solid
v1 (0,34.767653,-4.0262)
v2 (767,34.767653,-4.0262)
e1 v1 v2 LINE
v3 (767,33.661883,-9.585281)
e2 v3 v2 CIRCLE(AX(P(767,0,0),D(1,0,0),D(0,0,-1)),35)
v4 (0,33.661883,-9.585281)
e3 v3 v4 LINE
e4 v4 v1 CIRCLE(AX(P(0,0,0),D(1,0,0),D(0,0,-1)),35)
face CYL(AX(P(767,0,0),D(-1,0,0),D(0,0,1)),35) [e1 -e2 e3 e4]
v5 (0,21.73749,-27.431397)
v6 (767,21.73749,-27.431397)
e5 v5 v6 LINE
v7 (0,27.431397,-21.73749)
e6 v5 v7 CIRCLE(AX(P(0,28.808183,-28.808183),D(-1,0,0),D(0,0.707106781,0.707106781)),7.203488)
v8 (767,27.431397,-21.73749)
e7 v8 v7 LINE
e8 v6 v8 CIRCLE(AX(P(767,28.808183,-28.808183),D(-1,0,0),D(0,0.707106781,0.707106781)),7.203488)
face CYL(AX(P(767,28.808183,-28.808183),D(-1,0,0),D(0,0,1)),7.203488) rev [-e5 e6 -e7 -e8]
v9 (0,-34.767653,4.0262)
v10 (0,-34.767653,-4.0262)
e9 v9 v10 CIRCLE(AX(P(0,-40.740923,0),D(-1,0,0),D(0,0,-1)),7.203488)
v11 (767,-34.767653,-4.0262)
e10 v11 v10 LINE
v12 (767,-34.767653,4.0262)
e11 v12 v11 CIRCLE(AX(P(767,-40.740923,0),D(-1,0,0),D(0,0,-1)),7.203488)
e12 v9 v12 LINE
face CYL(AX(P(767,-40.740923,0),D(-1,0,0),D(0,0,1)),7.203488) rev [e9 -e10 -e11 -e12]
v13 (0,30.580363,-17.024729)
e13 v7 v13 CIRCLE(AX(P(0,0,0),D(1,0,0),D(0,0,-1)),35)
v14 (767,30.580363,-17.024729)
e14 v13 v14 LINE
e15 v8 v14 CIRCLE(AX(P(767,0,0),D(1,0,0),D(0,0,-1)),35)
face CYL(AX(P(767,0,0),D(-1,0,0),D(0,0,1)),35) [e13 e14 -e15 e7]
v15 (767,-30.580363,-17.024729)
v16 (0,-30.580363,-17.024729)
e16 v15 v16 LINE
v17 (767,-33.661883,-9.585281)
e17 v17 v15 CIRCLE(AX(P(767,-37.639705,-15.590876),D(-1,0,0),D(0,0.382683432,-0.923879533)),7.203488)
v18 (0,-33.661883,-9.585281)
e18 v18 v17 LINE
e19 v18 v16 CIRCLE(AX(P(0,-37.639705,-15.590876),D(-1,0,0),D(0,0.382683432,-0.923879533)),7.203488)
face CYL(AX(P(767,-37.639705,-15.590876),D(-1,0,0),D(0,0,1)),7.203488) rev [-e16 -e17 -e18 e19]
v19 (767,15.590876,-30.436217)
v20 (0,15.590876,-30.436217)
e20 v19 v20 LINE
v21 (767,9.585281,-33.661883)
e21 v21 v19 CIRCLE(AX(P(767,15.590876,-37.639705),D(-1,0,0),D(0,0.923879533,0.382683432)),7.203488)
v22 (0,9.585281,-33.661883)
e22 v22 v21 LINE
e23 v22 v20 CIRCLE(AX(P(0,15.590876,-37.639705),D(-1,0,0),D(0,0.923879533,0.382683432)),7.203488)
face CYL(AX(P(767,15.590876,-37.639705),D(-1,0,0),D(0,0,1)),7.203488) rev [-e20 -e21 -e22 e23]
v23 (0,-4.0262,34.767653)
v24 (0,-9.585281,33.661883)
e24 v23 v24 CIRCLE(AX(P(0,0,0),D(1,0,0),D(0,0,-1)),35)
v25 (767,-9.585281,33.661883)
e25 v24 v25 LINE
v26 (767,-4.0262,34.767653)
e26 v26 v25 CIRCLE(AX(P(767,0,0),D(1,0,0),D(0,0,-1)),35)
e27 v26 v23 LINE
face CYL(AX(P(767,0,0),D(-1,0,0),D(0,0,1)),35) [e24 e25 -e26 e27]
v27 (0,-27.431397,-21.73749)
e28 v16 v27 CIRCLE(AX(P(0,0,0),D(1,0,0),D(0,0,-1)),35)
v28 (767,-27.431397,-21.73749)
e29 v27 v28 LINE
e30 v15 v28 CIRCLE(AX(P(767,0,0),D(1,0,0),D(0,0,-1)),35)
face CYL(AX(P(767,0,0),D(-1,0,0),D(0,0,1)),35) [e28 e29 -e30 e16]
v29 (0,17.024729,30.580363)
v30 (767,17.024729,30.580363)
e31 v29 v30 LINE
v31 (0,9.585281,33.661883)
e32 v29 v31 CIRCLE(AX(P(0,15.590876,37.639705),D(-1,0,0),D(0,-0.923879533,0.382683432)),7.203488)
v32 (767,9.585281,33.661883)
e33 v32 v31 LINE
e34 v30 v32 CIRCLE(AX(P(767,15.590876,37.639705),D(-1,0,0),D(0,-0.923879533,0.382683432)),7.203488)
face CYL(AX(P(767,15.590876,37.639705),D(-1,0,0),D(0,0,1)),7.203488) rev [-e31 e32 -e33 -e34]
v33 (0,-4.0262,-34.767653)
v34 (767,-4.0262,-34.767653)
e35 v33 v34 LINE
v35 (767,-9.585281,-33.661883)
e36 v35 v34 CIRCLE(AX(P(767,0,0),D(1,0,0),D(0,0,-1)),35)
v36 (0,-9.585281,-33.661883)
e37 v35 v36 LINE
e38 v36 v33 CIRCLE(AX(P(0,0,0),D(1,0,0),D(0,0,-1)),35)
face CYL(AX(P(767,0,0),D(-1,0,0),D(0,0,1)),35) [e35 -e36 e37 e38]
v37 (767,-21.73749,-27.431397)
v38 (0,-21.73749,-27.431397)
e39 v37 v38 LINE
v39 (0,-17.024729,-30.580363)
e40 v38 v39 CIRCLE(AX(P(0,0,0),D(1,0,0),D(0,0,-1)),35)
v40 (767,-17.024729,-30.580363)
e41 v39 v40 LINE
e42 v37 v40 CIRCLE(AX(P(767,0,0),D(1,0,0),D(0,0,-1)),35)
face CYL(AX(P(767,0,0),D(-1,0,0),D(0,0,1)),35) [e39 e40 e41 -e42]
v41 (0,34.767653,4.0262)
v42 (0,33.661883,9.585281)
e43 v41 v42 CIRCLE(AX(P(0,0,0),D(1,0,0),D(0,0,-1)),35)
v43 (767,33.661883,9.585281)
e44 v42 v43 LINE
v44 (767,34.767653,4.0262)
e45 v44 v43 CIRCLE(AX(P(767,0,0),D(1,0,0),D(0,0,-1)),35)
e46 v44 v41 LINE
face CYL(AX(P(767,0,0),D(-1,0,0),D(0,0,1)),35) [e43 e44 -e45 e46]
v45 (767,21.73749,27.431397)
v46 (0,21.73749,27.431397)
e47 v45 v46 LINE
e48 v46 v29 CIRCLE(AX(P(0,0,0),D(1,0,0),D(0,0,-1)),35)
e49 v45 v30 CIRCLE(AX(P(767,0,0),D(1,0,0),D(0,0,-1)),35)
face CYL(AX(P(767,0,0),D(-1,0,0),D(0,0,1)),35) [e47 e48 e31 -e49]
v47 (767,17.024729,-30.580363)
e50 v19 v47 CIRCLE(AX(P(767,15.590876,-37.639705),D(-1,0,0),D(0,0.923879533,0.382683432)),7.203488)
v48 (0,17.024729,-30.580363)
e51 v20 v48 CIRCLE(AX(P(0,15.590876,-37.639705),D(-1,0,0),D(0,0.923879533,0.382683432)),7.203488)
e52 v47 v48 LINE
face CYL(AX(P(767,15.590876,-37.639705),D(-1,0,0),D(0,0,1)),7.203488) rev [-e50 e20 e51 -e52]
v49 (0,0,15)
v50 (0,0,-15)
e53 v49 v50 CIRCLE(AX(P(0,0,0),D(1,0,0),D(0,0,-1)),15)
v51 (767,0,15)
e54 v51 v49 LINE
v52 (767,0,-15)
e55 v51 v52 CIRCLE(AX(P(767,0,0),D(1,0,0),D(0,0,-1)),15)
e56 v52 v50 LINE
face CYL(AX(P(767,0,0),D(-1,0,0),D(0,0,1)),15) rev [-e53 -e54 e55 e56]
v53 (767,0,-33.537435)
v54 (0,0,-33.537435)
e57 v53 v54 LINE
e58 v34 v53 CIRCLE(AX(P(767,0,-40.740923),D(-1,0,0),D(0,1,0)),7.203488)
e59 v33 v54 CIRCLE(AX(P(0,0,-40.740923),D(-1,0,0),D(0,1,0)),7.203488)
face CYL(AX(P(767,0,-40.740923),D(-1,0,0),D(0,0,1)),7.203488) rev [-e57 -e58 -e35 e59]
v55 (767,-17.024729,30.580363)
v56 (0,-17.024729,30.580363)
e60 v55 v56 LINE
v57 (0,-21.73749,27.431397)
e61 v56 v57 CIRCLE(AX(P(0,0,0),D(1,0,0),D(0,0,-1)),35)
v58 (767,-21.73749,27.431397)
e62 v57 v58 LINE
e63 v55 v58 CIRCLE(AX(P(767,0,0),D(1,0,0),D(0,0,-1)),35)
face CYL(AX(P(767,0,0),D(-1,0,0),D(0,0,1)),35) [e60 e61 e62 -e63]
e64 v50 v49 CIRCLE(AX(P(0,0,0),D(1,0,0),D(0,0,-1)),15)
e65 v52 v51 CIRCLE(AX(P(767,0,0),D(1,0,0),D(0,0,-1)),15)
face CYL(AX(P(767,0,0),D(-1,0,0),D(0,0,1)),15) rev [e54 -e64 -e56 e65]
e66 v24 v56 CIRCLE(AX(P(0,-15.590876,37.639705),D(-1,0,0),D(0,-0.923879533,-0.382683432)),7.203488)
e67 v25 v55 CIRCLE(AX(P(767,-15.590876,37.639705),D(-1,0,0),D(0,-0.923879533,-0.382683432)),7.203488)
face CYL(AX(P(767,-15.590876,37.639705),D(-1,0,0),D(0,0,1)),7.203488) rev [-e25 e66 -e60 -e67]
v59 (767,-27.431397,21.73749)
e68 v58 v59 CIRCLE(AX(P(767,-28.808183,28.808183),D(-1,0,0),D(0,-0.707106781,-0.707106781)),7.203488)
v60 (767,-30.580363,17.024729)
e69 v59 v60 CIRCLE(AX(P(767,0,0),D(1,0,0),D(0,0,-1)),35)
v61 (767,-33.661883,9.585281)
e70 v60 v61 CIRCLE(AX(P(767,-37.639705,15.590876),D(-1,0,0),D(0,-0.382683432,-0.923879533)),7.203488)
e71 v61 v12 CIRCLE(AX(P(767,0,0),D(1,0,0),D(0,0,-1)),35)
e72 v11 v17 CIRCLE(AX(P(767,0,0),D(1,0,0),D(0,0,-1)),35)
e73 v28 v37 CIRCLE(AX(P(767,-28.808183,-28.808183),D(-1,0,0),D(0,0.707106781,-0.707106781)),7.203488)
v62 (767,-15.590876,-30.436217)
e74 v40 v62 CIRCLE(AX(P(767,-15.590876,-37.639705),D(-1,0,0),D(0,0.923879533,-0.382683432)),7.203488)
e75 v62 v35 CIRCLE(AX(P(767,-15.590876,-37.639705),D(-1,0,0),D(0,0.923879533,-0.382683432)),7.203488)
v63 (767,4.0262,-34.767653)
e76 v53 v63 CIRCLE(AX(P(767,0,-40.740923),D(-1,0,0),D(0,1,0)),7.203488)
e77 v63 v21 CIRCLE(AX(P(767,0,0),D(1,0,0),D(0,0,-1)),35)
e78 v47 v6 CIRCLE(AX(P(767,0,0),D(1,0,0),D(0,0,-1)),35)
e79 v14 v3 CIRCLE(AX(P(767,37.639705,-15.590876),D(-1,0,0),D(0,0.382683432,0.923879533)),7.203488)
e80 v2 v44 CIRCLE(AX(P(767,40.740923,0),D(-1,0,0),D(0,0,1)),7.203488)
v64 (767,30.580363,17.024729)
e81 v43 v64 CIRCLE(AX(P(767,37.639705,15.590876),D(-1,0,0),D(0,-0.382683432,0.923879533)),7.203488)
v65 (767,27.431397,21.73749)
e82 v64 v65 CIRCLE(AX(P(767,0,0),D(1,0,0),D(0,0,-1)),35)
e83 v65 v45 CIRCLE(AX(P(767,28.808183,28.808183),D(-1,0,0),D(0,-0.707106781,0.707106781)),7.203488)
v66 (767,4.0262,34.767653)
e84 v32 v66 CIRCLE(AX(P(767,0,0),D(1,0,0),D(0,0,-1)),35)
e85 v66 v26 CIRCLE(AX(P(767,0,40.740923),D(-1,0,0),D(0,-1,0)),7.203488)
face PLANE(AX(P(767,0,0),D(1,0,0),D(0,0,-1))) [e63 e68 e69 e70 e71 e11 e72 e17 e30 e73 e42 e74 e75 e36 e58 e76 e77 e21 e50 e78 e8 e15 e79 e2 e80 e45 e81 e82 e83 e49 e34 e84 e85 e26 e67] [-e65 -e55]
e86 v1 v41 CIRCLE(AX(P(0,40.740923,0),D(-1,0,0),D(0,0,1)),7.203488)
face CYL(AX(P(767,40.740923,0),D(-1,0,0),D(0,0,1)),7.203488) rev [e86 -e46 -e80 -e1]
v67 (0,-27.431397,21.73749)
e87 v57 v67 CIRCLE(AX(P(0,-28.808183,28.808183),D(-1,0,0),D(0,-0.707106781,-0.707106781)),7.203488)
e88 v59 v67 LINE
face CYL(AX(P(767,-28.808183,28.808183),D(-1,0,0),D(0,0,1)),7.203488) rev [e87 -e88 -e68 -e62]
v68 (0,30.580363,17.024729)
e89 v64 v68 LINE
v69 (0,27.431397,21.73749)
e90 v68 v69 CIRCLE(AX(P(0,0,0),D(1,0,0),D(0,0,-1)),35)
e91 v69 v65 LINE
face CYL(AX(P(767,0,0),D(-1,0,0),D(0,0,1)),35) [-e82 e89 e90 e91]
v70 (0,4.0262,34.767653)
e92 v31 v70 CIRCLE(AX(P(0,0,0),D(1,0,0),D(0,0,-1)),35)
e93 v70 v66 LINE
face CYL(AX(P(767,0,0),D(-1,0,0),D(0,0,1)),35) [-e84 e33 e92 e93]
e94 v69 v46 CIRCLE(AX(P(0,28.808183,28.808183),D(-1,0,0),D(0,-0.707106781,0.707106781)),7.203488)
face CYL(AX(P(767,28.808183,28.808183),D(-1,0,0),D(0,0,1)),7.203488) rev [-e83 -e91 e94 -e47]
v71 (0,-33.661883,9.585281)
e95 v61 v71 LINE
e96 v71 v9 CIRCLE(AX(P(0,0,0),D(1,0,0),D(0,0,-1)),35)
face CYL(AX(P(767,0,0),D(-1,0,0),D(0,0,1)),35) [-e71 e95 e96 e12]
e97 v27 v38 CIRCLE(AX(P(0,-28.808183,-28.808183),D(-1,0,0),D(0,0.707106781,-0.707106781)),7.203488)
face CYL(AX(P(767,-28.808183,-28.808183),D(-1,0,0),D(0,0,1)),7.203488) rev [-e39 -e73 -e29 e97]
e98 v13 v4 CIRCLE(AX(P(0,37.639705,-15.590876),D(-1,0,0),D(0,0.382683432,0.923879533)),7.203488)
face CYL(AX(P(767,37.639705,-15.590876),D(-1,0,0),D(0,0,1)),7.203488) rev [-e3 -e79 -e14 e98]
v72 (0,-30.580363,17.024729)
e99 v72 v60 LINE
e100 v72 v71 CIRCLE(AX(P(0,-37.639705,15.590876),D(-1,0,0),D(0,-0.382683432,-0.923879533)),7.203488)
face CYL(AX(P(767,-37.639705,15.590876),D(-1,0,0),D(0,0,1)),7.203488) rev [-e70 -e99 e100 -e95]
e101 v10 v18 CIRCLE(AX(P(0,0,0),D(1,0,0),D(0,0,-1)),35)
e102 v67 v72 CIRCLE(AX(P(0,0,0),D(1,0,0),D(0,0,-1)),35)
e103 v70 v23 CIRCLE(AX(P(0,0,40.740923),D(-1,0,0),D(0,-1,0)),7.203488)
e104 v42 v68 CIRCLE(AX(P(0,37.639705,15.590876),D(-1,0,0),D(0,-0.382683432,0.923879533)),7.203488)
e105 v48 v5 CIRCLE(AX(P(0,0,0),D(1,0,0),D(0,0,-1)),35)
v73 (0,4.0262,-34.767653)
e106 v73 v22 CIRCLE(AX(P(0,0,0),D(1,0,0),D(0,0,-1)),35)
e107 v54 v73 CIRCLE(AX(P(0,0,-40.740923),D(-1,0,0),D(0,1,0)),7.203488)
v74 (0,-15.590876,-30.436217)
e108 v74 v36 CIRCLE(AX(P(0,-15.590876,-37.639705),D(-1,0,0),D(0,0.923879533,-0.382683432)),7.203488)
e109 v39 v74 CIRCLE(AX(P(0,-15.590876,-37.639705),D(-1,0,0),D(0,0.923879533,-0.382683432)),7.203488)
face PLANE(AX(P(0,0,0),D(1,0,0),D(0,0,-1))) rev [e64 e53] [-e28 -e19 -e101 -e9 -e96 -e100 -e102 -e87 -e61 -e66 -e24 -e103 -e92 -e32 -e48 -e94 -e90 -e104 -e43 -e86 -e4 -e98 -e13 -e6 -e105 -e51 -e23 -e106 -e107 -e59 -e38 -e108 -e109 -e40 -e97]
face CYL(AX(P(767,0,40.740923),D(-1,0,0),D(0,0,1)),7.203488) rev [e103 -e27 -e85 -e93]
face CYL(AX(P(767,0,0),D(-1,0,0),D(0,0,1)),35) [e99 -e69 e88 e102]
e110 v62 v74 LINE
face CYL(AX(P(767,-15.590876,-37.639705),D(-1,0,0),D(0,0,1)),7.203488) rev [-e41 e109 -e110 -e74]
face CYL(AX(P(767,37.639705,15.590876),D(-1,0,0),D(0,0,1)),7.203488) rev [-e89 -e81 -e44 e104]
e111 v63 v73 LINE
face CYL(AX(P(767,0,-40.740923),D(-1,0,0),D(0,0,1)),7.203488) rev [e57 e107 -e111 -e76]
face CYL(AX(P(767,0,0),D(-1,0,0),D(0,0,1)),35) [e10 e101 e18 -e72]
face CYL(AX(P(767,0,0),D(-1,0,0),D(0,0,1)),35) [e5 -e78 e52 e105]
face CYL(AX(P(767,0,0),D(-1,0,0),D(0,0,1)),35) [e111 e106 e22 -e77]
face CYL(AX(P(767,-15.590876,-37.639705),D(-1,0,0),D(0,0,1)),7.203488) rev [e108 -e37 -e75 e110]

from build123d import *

# Parameters (mm, degrees)
SKETCH1_R                = 35
SKETCH1_R_2              = 15
BOSS_EXTRUDE2_DEPTH      = 767
SKETCH2_R                = 7.203487768
CUT_EXTRUDE1_DEPTH       = 767
PATTERN_CIRCULAR_1_COUNT = 16


with BuildPart() as part:
    # Sketch1 → Boss-Extrude2 (new body)
    with BuildSketch(Plane(origin=(0, 0, 0), x_dir=(0, 0, -1), z_dir=(1, 0, 0))):
        Circle(SKETCH1_R)
        Circle(SKETCH1_R_2, mode=Mode.SUBTRACT)
    extrude(amount=BOSS_EXTRUDE2_DEPTH)

    # Sketch2 → Cut-Extrude1 (cut)
    with BuildSketch(Plane.ZY):
        with Locations((0, 40.740922714)):
            Circle(SKETCH2_R)
    cut_extrude1 = extrude(amount=-CUT_EXTRUDE1_DEPTH, mode=Mode.SUBTRACT)

    # Pattern(Circular)1: Cut-Extrude1 ×16 about axis
    pattern_circular_1_axis = Axis((0, 0, 0), (1, 0, 0))
    for i in range(1, PATTERN_CIRCULAR_1_COUNT):
        add(cut_extrude1.rotate(pattern_circular_1_axis, i * 360 / PATTERN_CIRCULAR_1_COUNT), mode=Mode.SUBTRACT)


solid = part.part
